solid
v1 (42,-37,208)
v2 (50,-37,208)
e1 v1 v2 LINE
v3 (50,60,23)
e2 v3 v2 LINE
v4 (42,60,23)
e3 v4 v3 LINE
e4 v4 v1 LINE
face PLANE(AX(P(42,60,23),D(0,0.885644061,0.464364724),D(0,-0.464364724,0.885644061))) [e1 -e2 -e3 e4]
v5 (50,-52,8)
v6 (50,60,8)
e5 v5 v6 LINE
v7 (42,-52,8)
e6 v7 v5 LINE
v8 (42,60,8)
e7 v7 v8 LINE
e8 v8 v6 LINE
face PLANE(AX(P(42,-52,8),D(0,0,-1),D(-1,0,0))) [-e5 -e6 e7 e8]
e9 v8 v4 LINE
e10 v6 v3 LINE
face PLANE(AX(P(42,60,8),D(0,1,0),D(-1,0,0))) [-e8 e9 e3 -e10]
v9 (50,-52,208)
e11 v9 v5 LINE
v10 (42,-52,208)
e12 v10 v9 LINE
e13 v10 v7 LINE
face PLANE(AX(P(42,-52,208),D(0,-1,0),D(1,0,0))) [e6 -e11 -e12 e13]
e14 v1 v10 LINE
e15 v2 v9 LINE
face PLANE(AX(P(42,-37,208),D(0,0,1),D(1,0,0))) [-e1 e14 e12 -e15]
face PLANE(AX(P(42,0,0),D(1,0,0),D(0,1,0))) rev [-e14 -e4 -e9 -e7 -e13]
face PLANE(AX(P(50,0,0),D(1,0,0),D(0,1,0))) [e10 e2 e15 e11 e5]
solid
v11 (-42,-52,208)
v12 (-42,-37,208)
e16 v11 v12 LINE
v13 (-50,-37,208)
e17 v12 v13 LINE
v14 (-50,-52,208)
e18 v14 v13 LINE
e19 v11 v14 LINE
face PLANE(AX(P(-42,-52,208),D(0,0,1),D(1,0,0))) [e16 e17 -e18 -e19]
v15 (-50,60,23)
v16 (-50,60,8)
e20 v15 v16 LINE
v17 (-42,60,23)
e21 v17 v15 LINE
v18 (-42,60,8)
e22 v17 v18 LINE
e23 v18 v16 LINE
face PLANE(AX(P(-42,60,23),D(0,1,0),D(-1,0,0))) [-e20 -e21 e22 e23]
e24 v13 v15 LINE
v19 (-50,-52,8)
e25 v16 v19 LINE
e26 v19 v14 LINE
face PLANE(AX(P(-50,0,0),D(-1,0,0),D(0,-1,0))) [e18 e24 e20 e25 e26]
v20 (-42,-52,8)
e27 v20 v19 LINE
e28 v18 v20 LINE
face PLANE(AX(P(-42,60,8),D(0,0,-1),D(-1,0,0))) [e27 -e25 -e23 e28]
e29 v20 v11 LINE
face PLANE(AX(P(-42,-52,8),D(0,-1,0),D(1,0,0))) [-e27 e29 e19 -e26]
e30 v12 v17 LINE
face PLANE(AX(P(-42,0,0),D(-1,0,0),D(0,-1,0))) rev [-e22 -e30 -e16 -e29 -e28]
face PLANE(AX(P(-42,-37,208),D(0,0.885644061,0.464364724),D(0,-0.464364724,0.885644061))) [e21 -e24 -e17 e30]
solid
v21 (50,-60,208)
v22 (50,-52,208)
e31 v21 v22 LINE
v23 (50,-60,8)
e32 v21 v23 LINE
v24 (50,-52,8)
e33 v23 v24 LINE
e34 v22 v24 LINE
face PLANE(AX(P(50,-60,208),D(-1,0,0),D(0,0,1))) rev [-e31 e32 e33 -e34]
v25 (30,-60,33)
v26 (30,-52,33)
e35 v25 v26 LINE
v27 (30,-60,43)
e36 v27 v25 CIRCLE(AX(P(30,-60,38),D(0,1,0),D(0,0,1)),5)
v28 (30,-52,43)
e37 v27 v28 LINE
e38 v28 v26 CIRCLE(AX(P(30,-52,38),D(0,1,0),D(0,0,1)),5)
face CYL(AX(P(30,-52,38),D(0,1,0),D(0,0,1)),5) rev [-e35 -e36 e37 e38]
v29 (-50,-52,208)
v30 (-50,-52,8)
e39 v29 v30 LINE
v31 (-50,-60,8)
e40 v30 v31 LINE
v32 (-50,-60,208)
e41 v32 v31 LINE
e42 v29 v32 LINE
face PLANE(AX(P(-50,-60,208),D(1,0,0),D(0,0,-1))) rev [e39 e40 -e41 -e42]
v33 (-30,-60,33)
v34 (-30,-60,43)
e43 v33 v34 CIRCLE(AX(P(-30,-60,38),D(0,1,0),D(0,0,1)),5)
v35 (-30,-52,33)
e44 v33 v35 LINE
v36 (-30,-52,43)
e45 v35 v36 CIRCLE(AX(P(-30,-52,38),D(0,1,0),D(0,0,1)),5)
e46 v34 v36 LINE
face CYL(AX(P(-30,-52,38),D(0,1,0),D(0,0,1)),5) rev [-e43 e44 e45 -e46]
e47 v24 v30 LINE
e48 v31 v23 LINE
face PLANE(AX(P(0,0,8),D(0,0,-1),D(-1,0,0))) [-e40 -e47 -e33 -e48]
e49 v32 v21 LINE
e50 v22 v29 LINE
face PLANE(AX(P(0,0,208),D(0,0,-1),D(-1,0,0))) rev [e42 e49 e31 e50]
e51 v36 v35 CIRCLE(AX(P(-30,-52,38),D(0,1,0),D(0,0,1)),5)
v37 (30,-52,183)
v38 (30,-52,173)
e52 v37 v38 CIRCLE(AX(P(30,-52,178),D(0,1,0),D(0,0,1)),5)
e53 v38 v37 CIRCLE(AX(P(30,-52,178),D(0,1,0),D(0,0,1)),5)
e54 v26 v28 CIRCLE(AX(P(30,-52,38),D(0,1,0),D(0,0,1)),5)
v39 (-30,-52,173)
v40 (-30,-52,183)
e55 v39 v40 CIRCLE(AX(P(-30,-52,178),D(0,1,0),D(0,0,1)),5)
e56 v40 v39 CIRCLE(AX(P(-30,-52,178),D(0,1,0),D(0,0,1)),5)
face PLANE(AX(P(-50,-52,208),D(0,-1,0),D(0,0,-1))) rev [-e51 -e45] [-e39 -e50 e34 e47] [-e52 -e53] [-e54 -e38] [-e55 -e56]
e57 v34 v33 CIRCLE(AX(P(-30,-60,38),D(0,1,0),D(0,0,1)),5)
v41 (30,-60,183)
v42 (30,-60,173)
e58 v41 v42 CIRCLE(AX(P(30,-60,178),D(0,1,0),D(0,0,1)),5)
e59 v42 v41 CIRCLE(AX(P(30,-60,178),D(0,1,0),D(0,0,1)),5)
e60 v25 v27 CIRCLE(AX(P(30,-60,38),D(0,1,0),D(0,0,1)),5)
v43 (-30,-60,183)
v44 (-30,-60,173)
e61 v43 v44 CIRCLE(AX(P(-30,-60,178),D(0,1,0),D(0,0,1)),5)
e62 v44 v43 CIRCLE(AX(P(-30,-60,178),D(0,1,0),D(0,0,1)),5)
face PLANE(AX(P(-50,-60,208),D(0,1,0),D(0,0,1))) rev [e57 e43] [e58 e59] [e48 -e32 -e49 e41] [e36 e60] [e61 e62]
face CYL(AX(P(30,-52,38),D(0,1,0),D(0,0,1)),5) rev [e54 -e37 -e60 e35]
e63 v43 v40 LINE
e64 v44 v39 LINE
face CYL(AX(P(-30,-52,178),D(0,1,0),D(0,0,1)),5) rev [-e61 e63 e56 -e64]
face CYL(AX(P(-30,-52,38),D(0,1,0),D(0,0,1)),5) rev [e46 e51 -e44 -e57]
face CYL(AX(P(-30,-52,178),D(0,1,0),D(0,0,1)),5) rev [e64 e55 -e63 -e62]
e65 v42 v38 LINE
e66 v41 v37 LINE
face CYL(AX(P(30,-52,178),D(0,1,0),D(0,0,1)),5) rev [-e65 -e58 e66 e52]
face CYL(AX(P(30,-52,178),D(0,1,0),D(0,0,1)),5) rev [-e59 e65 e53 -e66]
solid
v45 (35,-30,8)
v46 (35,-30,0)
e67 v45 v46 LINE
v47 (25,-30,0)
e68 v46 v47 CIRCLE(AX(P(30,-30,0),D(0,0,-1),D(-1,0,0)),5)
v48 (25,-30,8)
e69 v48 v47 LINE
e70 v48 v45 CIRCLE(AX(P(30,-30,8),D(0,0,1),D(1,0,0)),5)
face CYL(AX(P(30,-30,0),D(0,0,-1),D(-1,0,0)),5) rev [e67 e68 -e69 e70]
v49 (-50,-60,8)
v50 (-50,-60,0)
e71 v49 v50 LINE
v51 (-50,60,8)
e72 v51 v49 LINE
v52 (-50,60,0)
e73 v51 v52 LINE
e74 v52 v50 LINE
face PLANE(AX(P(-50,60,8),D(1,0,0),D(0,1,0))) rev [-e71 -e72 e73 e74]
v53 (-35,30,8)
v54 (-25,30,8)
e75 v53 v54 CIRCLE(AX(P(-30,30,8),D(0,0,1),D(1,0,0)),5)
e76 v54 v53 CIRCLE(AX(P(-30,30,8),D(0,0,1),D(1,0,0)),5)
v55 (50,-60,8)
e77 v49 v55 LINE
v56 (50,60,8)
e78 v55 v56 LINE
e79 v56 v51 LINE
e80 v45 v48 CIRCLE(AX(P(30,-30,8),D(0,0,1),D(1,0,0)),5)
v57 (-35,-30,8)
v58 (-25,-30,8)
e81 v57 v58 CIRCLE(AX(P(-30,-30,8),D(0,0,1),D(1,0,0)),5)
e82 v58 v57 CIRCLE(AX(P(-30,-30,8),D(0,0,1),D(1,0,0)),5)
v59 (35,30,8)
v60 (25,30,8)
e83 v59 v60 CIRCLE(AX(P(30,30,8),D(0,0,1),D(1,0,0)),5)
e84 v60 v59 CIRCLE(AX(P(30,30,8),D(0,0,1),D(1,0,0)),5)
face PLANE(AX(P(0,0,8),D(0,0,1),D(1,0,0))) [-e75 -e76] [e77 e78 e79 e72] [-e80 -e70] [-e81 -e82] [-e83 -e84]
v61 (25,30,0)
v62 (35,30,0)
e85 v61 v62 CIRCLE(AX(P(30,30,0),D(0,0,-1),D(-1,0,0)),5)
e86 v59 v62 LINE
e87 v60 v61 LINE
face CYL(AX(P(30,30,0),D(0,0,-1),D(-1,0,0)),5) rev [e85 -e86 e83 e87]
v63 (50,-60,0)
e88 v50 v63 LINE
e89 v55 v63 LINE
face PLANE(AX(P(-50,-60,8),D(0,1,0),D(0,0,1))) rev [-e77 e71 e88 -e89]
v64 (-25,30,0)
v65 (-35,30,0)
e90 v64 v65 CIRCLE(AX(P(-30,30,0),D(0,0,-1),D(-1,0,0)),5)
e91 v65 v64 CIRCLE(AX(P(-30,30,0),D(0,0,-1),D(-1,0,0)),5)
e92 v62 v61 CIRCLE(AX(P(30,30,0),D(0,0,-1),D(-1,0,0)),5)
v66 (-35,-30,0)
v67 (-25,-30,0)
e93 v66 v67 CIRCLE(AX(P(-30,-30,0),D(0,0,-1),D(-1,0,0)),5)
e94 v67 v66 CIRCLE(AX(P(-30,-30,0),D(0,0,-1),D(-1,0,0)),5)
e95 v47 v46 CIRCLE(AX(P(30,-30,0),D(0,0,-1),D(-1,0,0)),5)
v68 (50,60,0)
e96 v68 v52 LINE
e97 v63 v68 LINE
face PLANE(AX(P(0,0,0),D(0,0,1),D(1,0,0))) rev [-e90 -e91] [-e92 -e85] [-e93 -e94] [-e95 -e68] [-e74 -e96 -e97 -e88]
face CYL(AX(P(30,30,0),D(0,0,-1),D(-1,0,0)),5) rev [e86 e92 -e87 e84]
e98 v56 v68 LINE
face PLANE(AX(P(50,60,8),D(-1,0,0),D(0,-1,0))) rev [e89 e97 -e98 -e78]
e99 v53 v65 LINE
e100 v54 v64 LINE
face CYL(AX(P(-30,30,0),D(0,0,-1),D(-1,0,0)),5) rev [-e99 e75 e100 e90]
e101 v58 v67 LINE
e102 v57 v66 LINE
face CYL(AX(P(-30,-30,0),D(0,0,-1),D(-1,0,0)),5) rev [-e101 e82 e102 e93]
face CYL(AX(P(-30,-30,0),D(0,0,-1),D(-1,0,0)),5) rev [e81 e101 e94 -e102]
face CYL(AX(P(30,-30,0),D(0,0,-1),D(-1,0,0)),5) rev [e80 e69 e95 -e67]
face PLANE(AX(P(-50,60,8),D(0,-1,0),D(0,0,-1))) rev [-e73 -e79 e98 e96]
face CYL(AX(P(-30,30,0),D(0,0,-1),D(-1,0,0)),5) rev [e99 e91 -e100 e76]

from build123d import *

# Parameters (mm, degrees)
SKETCH1_W                     = 100
SKETCH1_H                     = 120
BOSS_EXTRUDE1_DEPTH           = 8
SKETCH6_W                     = 100
SKETCH6_H                     = 8
BOSS_EXTRUDE4_DEPTH           = 200
BOSS_EXTRUDE2_DEPTH           = 8
BOSS_EXTRUDE3_DEPTH           = 8
M8_CLEARANCE_HOLE1_AT_2_COUNT = 2
M8_CLEARANCE_HOLE1_AT_2_PITCH = 60
M8_CLEARANCE_HOLE1_AT_3_COUNT = 2
M8_CLEARANCE_HOLE1_AT_3_PITCH = 140
M8_CLEARANCE_HOLE1_AT_4_COUNT = 2
M8_CLEARANCE_HOLE1_AT_4_PITCH = 152.315462117
M8_CLEARANCE_HOLE2_AT_2_COUNT = 2
M8_CLEARANCE_HOLE2_AT_2_PITCH = 60
M8_CLEARANCE_HOLE2_AT_3_COUNT = 2
M8_CLEARANCE_HOLE2_AT_3_PITCH = 84.852813742
M8_CLEARANCE_HOLE2_AT_4_COUNT = 2
M8_CLEARANCE_HOLE2_AT_4_PITCH = 60


with BuildPart() as part:
    # Sketch1 → Boss-Extrude1 (new body)
    with BuildSketch(Plane.XY):
        Rectangle(SKETCH1_W, SKETCH1_H)
    extrude(amount=BOSS_EXTRUDE1_DEPTH)

    # Sketch11 → M8 Clearance Hole2 (revolve, cut)
    with BuildSketch(Plane(origin=(30, 30, 0), x_dir=(0, 1, 0), z_dir=(1, 0, 0))):
        Polygon((0, 0), (0, 50.504303095), (5, 47.5), (5, 0), align=None)
    m8_clearance_hole2 = revolve(axis=Axis((30, 30, -6.35), (0, 0, 1)), mode=Mode.SUBTRACT)

    # M8 Clearance Hole2 at 2: M8 Clearance Hole2 ×2
    with Locations(*[(-i * M8_CLEARANCE_HOLE2_AT_2_PITCH, 0, 0) for i in range(1, M8_CLEARANCE_HOLE2_AT_2_COUNT)]):
        add(m8_clearance_hole2, mode=Mode.SUBTRACT)

    # M8 Clearance Hole2 at 3: M8 Clearance Hole2 ×2
    with Locations(*[Vector(-0.7071067811865478, -0.7071067811865474, 0) * (i * M8_CLEARANCE_HOLE2_AT_3_PITCH) for i in range(1, M8_CLEARANCE_HOLE2_AT_3_COUNT)]):
        add(m8_clearance_hole2, mode=Mode.SUBTRACT)

    # M8 Clearance Hole2 at 4: M8 Clearance Hole2 ×2
    with Locations(*[(0, -i * M8_CLEARANCE_HOLE2_AT_4_PITCH, 0) for i in range(1, M8_CLEARANCE_HOLE2_AT_4_COUNT)]):
        add(m8_clearance_hole2, mode=Mode.SUBTRACT)


with BuildPart() as body_2:
    # Sketch6 → Boss-Extrude4 (new body)
    with BuildSketch(Plane.XY.offset(8)):
        with Locations((0, -56)):
            Rectangle(SKETCH6_W, SKETCH6_H)
    extrude(amount=BOSS_EXTRUDE4_DEPTH)

    # Sketch8 → M8 Clearance Hole1 (revolve, cut)
    with BuildSketch(Plane(origin=(-30, -52, 38), x_dir=(0, 0, 1), z_dir=(1, 0, 0))):
        Polygon((0, 0), (0, 50.504303095), (5, 47.5), (5, 0), align=None)
    m8_clearance_hole1 = revolve(axis=Axis((-30, -45.65, 38), (0, -1, 0)), mode=Mode.SUBTRACT)

    # M8 Clearance Hole1 at 2: M8 Clearance Hole1 ×2
    with Locations(*[(i * M8_CLEARANCE_HOLE1_AT_2_PITCH, 0, 0) for i in range(1, M8_CLEARANCE_HOLE1_AT_2_COUNT)]):
        add(m8_clearance_hole1, mode=Mode.SUBTRACT)

    # M8 Clearance Hole1 at 3: M8 Clearance Hole1 ×2
    with Locations(*[(0, 0, i * M8_CLEARANCE_HOLE1_AT_3_PITCH) for i in range(1, M8_CLEARANCE_HOLE1_AT_3_COUNT)]):
        add(m8_clearance_hole1, mode=Mode.SUBTRACT)

    # M8 Clearance Hole1 at 4: M8 Clearance Hole1 ×2
    with Locations(*[Vector(0.39391929857916774, 0, 0.9191450300180579) * (i * M8_CLEARANCE_HOLE1_AT_4_PITCH) for i in range(1, M8_CLEARANCE_HOLE1_AT_4_COUNT)]):
        add(m8_clearance_hole1, mode=Mode.SUBTRACT)


with BuildPart() as body_3:
    # Sketch3 → Boss-Extrude2 (new body)
    with BuildSketch(Plane.ZY.offset(50)):
        Polygon((208, -52), (208, -37), (23, 60), (8, 60), (8, -52), align=None)
    extrude(amount=-BOSS_EXTRUDE2_DEPTH)


with BuildPart() as body_4:
    # Sketch4 → Boss-Extrude3 (new body)
    with BuildSketch(Plane(origin=(50, 0, 0), x_dir=(0, 0, -1), z_dir=(1, 0, 0))):
        Polygon((-8, -52), (-8, 60), (-23, 60), (-208, -37), (-208, -52), align=None)
    extrude(amount=-BOSS_EXTRUDE3_DEPTH)


solid = Compound([part.part, body_2.part, body_3.part, body_4.part])
